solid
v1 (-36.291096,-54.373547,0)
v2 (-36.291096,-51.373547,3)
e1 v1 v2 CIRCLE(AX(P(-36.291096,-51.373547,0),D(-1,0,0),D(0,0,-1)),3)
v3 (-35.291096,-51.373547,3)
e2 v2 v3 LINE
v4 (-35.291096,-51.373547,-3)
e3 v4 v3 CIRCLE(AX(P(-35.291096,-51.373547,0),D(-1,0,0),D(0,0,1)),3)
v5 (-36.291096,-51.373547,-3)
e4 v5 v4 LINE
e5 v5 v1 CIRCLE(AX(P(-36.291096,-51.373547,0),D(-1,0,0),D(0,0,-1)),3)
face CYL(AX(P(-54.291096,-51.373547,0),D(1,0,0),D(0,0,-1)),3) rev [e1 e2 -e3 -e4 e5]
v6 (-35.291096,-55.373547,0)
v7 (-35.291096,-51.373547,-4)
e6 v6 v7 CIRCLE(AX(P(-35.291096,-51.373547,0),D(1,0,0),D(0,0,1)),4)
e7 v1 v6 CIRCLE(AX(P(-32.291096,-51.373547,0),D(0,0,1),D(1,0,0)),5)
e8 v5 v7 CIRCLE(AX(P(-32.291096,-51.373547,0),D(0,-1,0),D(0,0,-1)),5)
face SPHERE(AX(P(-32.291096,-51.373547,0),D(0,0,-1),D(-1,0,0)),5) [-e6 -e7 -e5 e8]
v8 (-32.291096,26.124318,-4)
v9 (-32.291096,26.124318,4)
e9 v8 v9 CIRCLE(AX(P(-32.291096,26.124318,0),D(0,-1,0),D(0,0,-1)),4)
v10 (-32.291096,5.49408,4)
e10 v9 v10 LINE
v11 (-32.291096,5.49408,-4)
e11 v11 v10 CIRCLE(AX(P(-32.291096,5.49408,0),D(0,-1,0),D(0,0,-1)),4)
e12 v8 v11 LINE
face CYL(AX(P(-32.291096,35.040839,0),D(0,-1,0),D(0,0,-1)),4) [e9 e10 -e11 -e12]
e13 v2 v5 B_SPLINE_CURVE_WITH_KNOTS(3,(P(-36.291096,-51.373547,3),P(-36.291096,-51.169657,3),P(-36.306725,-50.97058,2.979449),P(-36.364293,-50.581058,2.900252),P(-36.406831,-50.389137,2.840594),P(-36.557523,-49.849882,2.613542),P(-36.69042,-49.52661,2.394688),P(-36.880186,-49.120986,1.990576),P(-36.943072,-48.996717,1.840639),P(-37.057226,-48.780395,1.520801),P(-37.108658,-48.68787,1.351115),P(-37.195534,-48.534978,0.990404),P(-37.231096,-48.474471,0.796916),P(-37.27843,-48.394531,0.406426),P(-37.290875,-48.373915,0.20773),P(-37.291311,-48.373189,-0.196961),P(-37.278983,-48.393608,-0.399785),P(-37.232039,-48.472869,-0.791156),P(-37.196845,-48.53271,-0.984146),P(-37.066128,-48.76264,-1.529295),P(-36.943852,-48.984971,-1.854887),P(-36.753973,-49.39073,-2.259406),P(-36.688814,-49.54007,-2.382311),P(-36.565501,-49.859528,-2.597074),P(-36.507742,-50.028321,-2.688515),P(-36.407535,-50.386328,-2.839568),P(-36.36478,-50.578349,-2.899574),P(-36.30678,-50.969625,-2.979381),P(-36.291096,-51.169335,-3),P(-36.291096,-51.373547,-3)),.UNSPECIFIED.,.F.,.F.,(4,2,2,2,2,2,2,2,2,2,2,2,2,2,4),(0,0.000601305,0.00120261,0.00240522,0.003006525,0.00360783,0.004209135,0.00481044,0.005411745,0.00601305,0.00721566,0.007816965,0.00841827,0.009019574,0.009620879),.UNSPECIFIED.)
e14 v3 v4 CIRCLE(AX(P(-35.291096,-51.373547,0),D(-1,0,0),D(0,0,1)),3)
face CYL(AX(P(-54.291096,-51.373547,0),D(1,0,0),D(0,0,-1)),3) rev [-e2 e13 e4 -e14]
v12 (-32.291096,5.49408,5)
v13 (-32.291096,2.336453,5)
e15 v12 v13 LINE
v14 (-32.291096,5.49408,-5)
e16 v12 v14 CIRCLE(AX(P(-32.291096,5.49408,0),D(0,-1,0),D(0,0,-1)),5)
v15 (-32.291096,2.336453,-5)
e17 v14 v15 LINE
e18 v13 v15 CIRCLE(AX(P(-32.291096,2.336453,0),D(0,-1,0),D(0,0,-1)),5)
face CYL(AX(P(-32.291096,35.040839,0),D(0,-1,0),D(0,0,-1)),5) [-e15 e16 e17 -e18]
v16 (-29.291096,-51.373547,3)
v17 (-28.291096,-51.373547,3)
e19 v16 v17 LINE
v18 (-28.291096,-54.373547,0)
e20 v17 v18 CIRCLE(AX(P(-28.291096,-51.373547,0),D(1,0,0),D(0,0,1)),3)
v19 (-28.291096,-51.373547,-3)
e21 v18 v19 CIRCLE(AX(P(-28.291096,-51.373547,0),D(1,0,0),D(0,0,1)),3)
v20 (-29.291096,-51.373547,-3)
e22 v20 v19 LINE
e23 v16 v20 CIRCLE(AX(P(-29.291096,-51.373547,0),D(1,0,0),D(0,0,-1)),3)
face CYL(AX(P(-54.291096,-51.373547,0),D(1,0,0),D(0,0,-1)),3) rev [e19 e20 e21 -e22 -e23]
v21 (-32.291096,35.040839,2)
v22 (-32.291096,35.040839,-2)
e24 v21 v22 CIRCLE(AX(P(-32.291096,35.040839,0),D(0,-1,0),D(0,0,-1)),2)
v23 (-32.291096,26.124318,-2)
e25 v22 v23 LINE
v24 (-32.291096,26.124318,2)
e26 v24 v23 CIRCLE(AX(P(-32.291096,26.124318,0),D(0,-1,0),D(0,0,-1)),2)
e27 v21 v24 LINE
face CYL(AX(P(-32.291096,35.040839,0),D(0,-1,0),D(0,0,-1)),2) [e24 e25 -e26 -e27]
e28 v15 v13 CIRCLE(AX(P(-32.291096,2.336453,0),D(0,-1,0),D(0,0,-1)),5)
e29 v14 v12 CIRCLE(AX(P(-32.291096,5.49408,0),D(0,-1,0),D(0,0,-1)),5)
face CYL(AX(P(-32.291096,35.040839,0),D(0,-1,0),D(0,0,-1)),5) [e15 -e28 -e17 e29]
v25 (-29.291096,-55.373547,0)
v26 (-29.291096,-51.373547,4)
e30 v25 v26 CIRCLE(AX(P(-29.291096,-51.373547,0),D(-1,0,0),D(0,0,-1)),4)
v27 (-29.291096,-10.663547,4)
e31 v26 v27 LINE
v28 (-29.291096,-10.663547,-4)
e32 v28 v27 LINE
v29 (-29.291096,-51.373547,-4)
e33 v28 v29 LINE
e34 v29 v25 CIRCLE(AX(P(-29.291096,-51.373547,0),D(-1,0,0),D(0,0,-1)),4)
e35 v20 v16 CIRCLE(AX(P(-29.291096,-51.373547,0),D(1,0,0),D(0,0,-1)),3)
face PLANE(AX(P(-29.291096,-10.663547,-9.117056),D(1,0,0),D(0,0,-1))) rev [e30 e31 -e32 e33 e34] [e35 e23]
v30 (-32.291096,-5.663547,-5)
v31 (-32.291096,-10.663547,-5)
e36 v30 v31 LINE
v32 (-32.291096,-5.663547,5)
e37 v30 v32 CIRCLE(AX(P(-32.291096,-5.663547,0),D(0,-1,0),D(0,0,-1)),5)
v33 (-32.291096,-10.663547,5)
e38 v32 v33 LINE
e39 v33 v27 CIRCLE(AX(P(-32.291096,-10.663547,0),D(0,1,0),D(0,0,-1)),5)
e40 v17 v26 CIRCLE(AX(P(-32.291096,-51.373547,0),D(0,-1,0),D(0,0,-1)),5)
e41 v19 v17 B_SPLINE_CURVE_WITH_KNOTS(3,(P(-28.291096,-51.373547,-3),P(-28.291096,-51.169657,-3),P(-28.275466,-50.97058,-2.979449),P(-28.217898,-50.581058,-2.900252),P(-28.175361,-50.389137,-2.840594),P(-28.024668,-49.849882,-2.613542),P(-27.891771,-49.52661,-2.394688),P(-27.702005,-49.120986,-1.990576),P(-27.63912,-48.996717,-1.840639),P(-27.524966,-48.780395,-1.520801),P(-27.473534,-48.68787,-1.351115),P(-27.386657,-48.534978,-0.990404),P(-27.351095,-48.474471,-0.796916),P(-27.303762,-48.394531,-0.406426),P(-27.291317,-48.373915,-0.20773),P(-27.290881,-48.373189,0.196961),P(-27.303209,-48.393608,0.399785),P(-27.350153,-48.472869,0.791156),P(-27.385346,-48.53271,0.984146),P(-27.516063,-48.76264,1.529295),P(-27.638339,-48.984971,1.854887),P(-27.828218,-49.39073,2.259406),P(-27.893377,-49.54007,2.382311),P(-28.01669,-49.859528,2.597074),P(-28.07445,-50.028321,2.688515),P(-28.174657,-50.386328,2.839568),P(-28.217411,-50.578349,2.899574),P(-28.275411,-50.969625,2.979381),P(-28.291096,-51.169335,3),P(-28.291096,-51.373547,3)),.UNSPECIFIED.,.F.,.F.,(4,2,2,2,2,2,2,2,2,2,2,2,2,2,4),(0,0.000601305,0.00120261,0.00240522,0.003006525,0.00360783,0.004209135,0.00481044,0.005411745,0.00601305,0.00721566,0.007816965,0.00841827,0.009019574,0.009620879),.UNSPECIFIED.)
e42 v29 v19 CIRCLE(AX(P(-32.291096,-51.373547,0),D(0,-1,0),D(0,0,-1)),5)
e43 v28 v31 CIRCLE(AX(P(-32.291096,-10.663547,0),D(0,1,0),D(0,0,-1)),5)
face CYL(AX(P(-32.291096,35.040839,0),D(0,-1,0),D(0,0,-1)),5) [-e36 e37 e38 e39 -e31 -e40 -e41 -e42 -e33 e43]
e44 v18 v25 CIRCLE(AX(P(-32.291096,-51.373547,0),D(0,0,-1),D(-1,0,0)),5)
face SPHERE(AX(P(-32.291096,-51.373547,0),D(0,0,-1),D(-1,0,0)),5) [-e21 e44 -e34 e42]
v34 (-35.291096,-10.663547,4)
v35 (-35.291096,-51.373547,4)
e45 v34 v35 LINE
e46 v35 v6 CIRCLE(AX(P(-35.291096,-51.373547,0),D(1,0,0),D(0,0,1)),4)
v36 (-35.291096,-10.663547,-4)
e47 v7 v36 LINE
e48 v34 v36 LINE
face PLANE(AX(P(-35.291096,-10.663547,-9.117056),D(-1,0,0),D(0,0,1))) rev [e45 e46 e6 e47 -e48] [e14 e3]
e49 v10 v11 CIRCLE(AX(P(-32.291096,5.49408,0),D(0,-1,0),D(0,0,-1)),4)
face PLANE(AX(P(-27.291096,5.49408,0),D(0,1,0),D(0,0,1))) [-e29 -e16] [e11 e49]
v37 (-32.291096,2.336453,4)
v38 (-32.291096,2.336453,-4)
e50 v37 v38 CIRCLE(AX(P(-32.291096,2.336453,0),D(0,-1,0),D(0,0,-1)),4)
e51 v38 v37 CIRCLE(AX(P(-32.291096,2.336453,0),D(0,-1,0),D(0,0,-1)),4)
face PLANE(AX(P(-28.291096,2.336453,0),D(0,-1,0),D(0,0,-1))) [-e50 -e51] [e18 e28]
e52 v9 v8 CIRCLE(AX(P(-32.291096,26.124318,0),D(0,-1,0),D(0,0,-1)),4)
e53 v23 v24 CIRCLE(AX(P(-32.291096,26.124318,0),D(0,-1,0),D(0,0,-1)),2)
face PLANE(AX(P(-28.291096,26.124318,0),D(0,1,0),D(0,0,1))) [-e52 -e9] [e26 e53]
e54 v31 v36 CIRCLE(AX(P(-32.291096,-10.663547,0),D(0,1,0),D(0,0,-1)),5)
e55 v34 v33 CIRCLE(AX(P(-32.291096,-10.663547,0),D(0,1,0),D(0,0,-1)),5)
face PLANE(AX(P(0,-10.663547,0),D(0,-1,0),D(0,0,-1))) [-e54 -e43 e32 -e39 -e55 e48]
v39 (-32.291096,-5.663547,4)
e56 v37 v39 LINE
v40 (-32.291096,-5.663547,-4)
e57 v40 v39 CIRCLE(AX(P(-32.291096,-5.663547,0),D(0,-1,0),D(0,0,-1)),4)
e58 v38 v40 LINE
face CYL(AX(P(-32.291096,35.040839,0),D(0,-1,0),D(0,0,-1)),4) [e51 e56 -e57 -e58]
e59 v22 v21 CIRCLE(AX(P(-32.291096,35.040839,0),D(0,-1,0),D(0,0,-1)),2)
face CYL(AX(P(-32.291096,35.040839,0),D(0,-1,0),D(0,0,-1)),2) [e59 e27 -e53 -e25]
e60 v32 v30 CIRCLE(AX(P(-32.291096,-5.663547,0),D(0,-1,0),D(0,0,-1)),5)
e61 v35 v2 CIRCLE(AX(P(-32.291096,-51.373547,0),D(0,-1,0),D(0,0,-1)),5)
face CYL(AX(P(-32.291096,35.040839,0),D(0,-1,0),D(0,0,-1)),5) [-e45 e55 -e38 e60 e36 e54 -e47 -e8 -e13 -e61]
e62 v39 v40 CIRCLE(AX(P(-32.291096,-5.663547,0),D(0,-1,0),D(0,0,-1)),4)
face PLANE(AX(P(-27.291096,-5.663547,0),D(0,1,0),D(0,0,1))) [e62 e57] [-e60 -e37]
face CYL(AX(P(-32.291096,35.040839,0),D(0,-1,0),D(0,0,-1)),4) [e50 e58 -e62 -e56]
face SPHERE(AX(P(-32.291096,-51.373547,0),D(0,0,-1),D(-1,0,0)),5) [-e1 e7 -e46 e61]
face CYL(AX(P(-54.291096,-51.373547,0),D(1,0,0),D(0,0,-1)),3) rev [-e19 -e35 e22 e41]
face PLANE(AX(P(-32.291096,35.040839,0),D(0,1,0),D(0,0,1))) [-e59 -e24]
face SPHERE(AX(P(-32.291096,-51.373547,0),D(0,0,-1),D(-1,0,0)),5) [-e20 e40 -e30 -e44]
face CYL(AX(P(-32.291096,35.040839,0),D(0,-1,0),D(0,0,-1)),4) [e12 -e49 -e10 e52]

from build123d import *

# Parameters (mm, degrees)
SKETCH2_W               = 6
SKETCH2_H               = 15
CUT_EXTRUDE1_DEPTH      = 45.71
CUT_EXTRUDE2_DEPTH      = 57.171431365
CUT_EXTRUDE2_DEPTH_BACK = 19
SKETCH4_R               = 3


with BuildPart() as part:
    # Model → Revolve1 (revolve)
    with BuildSketch(Plane.XY, mode=Mode.PRIVATE) as revolve1_sk:
        with BuildLine():
            Line((-27.291095715, -5.663546948), (-27.291095715, -10.663546948))
            Line((-27.291095715, -10.663546948), (-27.291095715, -51.373546948))
            ThreePointArc((-27.291095715, -51.373546948), (-28.755561809, -54.909080854), (-32.291095715, -56.373546948))
            Line((-32.291095715, -56.373546948), (-32.291095715, -52.264917369))
            Line((-32.291095715, -52.264917369), (-32.291095715, -10.663546948))
            Line((-32.291095715, -10.663546948), (-32.291095715, 35.040839423))
            Line((-32.291095715, 35.040839423), (-30.291095715, 35.040839423))
            Line((-30.291095715, 35.040839423), (-30.291095715, 26.12431753))
            Line((-30.291095715, 26.12431753), (-28.291095715, 26.12431753))
            Line((-28.291095715, 26.12431753), (-28.291095715, 5.494079969))
            Line((-28.291095715, 5.494079969), (-27.291095715, 5.494079969))
            Line((-27.291095715, 5.494079969), (-27.291095715, 2.336453052))
            Line((-27.291095715, 2.336453052), (-28.291095714, 2.336453052))
            Line((-28.291095714, 2.336453052), (-28.291095714, -5.663546948))
            Line((-28.291095714, -5.663546948), (-27.291095715, -5.663546948))
        make_face()
    revolve(revolve1_sk.sketch.rotate(Axis((-32.291095715, 35.040839423, 0), (0, 1, 0)), 90), axis=Axis((-32.291095715, 35.040839423, 0), (0, 1, 0)))

    # Sketch2 → Cut-Extrude1 (cut)
    with BuildSketch(Plane(origin=(0, -56.373546948, 0), x_dir=(-1, 0, 0), z_dir=(0, -1, 0))):
        with Locations((32.291095715, 1.617056414)):
            Rectangle(SKETCH2_W, SKETCH2_H)
    extrude(amount=-CUT_EXTRUDE1_DEPTH, mode=Mode.SUBTRACT)

    # Sketch4 → Cut-Extrude2 (cut, two sides: drawn at the far end of the back side and taken through both)
    with BuildSketch(Plane(origin=(-35.291095715, 0, 0), x_dir=(0, 0, -1), z_dir=(1, 0, 0)).offset(-CUT_EXTRUDE2_DEPTH_BACK)):
        with Locations(Location((0, -51.373546948, 0), (0, 0, 180))):
            Circle(SKETCH4_R)
    extrude(amount=CUT_EXTRUDE2_DEPTH + CUT_EXTRUDE2_DEPTH_BACK, mode=Mode.SUBTRACT)


solid = part.part
